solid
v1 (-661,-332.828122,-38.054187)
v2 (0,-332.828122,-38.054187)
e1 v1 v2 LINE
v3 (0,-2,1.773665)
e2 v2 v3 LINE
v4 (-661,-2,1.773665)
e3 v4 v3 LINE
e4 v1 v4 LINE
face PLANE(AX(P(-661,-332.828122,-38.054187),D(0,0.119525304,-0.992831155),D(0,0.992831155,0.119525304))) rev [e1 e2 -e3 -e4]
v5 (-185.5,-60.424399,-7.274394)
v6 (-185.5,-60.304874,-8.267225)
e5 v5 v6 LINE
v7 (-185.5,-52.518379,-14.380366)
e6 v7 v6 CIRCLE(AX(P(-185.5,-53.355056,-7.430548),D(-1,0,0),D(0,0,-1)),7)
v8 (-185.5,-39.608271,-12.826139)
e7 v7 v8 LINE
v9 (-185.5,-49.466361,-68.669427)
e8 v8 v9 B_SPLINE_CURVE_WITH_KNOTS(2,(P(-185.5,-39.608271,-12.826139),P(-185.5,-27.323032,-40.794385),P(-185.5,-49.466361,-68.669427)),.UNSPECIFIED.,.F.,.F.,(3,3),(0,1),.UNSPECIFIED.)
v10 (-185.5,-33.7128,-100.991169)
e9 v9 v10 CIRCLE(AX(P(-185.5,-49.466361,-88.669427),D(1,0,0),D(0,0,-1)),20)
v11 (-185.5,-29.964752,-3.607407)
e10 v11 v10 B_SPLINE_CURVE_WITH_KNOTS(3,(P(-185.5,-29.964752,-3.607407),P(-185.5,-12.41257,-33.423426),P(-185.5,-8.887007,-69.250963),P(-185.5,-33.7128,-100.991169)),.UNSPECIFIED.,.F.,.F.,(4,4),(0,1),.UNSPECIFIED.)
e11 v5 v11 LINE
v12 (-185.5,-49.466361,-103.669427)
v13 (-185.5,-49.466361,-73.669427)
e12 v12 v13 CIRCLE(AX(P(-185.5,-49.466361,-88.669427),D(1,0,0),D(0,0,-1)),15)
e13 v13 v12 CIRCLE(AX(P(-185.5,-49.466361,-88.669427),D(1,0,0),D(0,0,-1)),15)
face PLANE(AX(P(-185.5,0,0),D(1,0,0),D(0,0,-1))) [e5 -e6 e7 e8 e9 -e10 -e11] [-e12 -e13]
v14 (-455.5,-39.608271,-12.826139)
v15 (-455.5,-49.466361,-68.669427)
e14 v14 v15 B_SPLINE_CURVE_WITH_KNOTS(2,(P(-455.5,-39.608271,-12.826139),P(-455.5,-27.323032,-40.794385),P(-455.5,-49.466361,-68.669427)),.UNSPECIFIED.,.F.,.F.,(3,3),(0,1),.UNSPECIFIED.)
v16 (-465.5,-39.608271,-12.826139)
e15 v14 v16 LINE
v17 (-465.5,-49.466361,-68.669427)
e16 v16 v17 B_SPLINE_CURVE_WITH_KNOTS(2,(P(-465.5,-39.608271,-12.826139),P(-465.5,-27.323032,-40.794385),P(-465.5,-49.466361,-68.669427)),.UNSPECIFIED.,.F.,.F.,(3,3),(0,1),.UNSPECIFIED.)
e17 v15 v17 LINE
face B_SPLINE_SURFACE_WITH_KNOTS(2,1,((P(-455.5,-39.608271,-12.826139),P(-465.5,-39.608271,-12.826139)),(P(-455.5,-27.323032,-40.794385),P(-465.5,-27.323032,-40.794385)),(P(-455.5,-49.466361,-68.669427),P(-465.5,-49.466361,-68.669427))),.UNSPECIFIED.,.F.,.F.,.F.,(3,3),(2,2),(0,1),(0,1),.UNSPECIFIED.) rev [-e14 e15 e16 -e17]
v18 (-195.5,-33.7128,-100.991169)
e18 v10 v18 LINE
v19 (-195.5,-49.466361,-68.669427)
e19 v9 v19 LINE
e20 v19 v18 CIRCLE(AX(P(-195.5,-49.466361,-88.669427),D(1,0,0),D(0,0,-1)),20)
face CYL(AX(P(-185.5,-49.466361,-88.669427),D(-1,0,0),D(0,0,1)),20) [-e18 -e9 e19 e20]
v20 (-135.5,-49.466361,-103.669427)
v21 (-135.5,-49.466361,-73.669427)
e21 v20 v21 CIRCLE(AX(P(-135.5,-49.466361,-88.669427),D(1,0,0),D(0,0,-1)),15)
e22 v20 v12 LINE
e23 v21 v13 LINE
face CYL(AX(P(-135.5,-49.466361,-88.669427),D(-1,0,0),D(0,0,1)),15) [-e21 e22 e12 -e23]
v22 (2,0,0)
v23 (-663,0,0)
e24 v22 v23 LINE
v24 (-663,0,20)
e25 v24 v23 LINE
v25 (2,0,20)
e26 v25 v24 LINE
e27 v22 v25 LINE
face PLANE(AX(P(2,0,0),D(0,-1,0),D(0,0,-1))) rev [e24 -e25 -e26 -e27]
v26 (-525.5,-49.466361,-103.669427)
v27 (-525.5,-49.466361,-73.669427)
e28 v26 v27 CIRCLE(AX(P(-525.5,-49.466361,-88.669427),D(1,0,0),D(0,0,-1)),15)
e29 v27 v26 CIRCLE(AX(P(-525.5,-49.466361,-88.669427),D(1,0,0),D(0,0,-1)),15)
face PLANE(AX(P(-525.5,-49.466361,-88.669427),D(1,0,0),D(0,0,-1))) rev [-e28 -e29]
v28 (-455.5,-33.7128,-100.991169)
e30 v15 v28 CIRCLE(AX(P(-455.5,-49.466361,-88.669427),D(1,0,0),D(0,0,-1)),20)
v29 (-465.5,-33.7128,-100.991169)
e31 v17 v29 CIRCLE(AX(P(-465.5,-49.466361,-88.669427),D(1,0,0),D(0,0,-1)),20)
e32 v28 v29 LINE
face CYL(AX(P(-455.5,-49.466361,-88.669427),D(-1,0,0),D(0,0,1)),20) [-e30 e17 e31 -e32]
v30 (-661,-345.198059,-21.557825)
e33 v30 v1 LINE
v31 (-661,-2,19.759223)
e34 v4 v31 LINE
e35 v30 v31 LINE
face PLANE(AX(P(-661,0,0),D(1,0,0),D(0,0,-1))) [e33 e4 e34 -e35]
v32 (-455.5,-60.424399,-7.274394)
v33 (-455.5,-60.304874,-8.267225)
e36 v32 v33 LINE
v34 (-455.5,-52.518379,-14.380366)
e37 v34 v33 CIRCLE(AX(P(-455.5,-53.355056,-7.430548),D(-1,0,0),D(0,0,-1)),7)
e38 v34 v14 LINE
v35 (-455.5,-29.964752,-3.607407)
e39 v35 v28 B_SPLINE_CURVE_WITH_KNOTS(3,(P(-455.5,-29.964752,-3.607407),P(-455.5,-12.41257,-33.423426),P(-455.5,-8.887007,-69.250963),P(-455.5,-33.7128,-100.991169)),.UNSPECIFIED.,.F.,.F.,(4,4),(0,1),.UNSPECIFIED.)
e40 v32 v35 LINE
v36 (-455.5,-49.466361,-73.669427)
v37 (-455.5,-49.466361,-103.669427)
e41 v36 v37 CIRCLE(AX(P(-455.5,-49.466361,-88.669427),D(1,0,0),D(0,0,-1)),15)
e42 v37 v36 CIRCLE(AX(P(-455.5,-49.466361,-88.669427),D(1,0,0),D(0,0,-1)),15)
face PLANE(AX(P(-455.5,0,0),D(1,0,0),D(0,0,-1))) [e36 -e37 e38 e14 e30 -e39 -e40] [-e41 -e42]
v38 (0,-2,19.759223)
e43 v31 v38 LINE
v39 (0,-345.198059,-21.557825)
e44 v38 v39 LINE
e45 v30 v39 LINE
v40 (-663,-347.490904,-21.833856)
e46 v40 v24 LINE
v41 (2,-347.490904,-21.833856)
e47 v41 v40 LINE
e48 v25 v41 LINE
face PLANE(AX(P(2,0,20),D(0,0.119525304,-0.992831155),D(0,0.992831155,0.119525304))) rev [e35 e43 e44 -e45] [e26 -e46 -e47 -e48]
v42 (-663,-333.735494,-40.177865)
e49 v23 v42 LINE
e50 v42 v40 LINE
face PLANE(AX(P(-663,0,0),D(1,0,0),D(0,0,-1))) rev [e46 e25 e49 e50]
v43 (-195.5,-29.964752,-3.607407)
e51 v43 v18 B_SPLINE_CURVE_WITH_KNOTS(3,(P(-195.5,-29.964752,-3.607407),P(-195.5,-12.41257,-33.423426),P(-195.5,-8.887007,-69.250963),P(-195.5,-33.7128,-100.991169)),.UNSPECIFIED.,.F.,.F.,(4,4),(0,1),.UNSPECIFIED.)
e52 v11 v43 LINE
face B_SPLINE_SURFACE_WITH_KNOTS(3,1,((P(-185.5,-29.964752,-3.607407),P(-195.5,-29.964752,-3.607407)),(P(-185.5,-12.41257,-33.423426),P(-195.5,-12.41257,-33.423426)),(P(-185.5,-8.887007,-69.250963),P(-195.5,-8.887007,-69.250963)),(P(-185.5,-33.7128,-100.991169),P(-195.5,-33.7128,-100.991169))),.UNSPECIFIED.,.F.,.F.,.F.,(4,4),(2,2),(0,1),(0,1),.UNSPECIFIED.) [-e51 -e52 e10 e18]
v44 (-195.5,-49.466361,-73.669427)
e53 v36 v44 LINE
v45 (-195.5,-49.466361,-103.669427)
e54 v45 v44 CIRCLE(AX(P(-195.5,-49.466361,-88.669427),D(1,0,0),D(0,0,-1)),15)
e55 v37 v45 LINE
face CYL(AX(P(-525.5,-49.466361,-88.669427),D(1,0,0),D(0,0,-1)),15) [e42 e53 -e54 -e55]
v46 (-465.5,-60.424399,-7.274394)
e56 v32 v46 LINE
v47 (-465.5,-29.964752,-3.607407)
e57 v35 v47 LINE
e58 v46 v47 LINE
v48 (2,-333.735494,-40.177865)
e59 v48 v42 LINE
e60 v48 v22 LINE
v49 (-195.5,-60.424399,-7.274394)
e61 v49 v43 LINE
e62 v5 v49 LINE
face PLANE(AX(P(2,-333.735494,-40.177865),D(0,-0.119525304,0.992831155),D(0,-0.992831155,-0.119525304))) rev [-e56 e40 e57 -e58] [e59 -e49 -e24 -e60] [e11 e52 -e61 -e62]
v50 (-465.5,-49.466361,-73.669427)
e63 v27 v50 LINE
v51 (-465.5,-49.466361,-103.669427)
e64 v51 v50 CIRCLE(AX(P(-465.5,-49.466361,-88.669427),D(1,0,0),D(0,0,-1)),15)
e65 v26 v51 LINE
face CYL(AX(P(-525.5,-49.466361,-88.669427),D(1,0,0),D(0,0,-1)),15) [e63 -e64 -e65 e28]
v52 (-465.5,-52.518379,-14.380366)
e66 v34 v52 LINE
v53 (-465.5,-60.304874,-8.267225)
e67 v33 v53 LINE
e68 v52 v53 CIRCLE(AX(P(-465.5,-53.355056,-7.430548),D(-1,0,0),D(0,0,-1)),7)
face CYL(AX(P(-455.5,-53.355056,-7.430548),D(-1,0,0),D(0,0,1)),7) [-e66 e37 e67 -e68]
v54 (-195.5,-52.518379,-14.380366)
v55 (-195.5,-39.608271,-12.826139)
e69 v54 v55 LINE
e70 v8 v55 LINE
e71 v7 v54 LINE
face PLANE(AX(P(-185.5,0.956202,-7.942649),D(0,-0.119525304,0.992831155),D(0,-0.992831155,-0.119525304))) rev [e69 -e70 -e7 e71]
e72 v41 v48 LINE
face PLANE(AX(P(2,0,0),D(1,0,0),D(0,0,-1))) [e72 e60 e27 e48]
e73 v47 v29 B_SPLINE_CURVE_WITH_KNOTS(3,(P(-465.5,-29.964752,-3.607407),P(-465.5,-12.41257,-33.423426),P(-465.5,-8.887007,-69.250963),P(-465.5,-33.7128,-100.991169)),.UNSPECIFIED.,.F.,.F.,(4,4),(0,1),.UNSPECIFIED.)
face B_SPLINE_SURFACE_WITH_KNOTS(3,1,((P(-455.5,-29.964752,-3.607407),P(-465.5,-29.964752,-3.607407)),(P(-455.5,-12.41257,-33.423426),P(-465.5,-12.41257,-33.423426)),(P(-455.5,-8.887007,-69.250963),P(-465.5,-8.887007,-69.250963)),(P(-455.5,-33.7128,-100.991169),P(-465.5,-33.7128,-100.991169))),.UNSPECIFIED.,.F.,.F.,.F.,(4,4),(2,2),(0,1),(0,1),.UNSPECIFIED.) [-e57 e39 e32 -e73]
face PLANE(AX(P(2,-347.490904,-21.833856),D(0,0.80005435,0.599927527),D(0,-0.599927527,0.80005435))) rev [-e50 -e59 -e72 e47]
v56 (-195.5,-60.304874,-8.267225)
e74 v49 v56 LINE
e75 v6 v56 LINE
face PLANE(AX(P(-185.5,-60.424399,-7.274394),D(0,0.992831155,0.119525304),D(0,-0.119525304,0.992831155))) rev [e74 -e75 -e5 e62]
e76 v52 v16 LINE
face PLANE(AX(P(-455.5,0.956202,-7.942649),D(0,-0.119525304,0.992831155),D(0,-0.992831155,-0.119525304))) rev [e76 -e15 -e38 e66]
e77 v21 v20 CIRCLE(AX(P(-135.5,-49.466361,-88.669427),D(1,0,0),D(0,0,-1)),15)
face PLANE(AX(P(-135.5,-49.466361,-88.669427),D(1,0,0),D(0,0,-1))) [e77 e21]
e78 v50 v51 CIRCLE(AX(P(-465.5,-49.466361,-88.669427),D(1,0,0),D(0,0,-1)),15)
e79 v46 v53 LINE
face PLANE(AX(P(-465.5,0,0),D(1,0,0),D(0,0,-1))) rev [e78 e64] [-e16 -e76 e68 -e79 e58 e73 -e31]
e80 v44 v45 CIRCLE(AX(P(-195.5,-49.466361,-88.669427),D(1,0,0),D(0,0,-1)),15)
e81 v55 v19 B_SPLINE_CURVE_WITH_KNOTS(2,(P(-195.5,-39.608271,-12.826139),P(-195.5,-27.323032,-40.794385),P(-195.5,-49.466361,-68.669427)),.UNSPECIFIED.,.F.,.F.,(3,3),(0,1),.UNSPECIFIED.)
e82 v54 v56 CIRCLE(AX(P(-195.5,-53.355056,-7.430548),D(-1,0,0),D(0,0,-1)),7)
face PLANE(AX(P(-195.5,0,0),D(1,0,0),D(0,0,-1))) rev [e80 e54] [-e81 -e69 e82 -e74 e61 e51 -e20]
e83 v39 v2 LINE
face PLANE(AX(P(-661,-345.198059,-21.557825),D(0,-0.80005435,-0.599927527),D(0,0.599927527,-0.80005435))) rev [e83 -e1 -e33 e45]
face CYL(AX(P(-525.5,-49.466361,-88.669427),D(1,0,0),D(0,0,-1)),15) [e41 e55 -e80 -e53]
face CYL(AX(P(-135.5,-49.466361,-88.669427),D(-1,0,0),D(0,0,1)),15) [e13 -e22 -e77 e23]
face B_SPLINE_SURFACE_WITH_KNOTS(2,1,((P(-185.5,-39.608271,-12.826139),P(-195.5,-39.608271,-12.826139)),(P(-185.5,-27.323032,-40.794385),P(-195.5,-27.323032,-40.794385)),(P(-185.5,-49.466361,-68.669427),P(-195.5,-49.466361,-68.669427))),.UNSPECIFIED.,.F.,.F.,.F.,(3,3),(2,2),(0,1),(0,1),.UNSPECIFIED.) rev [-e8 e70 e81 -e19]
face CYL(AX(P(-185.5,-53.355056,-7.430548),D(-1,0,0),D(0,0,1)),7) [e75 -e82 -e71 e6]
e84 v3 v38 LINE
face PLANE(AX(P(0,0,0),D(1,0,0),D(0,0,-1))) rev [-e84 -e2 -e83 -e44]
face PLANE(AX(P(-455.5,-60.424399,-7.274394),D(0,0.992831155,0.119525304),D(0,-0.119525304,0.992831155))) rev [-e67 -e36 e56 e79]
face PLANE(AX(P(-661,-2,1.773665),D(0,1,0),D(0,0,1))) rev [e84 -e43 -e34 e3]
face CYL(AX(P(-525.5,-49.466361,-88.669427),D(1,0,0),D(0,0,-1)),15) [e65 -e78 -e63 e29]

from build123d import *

# Parameters (mm, degrees)
BOSS_EXTRUDE1_DEPTH = 2
BOSS_EXTRUDE2_DEPTH = 661
BOSS_EXTRUDE3_DEPTH = 2
SKETCH4_R           = 15
BOSS_EXTRUDE4_DEPTH = 10
LPATTERN1_COUNT     = 2
LPATTERN1_PITCH     = 270
SKETCH5_R           = 15
BOSS_EXTRUDE5_DEPTH = 340
SKETCH6_R           = 15
BOSS_EXTRUDE6_DEPTH = 50


with BuildPart() as part:
    # Sketch1 → Boss-Extrude1 (new body)
    with BuildSketch(Plane(origin=(0, 0, 0), x_dir=(0, 0, -1), z_dir=(1, 0, 0))):
        Polygon((0, 0), (-20, 0), (21.83385642, -347.490904136), (40.177865273, -333.735493803), align=None)
    extrude(amount=BOSS_EXTRUDE1_DEPTH)

    # Sketch2 → Boss-Extrude2 (add)
    with BuildSketch(Plane.ZY):
        Polygon((0, 0), (20, 0), (19.759223301, -2), (1.773664518, -2), (-38.054187031, -332.828121742), (-21.557824554, -345.198058798), (-21.83385642, -347.490904136), (-40.177865273, -333.735493803), align=None)
    extrude(amount=BOSS_EXTRUDE2_DEPTH)

    # Sketch3 → Boss-Extrude3 (add)
    with BuildSketch(Plane.ZY.offset(661)):
        Polygon((20, 0), (0, 0), (-40.177865273, -333.735493803), (-21.83385642, -347.490904136), align=None)
    extrude(amount=BOSS_EXTRUDE3_DEPTH)

    # Sketch4 → Boss-Extrude4 (add)
    with BuildSketch(Plane(origin=(-195.5, 0, 0), x_dir=(0, 0, -1), z_dir=(1, 0, 0))):
        with BuildLine():
            Line((3.607407095, -29.964752484), (7.274393684, -60.424399152))
            Line((7.274393684, -60.424399152), (8.267224839, -60.304873847))
            ThreePointArc((8.267224839, -60.304873847), (12.936431276, -57.677699188), (14.380365793, -52.518378636))
            Line((14.380365793, -52.518378636), (12.826139197, -39.608270621))
            add(Edge.make_bspline(
                [(12.826139197, -39.608270621), (40.794384715, -27.323032004), (68.669426918, -49.466360803)],
                knots=[0, 0, 0, 1, 1, 1], degree=2))
            ThreePointArc((68.669426918, -49.466360803), (97.431993806, -67.44460937), (100.991169072, -33.712800243))
            add(Edge.make_bspline(
                [(3.607407095, -29.964752484), (33.423426205, -12.412570219), (69.250962672, -8.887006882), (100.991169072, -33.712800243)],
                knots=[0, 0, 0, 0, 1, 1, 1, 1], degree=3))
        make_face()
        with Locations((88.669426918, -49.466360803)):
            Circle(SKETCH4_R, mode=Mode.SUBTRACT)
    boss_extrude4 = extrude(amount=BOSS_EXTRUDE4_DEPTH)

    # LPattern1: Boss-Extrude4 ×2
    with Locations(*[(-i * LPATTERN1_PITCH, 0, 0) for i in range(1, LPATTERN1_COUNT)]):
        add(boss_extrude4)



with BuildPart() as body_2:
    # Sketch5 → Boss-Extrude5 (new body)
    with BuildSketch(Plane(origin=(-185.5, 0, 0), x_dir=(0, 0, -1), z_dir=(1, 0, 0))):
        with Locations((88.669426918, -49.466360803)):
            Circle(SKETCH5_R)
    extrude(amount=-BOSS_EXTRUDE5_DEPTH)


with BuildPart() as part_1:
    add(part.part)

    add(body_2.part)  # Boss-Extrude6 merges body 2
    # Sketch6 → Boss-Extrude6 (add)
    with BuildSketch(Plane(origin=(-185.5, 0, 0), x_dir=(0, 0, -1), z_dir=(1, 0, 0))):
        with Locations((88.669426918, -49.466360803)):
            Circle(SKETCH6_R)
    extrude(amount=BOSS_EXTRUDE6_DEPTH)


solid = part_1.part
